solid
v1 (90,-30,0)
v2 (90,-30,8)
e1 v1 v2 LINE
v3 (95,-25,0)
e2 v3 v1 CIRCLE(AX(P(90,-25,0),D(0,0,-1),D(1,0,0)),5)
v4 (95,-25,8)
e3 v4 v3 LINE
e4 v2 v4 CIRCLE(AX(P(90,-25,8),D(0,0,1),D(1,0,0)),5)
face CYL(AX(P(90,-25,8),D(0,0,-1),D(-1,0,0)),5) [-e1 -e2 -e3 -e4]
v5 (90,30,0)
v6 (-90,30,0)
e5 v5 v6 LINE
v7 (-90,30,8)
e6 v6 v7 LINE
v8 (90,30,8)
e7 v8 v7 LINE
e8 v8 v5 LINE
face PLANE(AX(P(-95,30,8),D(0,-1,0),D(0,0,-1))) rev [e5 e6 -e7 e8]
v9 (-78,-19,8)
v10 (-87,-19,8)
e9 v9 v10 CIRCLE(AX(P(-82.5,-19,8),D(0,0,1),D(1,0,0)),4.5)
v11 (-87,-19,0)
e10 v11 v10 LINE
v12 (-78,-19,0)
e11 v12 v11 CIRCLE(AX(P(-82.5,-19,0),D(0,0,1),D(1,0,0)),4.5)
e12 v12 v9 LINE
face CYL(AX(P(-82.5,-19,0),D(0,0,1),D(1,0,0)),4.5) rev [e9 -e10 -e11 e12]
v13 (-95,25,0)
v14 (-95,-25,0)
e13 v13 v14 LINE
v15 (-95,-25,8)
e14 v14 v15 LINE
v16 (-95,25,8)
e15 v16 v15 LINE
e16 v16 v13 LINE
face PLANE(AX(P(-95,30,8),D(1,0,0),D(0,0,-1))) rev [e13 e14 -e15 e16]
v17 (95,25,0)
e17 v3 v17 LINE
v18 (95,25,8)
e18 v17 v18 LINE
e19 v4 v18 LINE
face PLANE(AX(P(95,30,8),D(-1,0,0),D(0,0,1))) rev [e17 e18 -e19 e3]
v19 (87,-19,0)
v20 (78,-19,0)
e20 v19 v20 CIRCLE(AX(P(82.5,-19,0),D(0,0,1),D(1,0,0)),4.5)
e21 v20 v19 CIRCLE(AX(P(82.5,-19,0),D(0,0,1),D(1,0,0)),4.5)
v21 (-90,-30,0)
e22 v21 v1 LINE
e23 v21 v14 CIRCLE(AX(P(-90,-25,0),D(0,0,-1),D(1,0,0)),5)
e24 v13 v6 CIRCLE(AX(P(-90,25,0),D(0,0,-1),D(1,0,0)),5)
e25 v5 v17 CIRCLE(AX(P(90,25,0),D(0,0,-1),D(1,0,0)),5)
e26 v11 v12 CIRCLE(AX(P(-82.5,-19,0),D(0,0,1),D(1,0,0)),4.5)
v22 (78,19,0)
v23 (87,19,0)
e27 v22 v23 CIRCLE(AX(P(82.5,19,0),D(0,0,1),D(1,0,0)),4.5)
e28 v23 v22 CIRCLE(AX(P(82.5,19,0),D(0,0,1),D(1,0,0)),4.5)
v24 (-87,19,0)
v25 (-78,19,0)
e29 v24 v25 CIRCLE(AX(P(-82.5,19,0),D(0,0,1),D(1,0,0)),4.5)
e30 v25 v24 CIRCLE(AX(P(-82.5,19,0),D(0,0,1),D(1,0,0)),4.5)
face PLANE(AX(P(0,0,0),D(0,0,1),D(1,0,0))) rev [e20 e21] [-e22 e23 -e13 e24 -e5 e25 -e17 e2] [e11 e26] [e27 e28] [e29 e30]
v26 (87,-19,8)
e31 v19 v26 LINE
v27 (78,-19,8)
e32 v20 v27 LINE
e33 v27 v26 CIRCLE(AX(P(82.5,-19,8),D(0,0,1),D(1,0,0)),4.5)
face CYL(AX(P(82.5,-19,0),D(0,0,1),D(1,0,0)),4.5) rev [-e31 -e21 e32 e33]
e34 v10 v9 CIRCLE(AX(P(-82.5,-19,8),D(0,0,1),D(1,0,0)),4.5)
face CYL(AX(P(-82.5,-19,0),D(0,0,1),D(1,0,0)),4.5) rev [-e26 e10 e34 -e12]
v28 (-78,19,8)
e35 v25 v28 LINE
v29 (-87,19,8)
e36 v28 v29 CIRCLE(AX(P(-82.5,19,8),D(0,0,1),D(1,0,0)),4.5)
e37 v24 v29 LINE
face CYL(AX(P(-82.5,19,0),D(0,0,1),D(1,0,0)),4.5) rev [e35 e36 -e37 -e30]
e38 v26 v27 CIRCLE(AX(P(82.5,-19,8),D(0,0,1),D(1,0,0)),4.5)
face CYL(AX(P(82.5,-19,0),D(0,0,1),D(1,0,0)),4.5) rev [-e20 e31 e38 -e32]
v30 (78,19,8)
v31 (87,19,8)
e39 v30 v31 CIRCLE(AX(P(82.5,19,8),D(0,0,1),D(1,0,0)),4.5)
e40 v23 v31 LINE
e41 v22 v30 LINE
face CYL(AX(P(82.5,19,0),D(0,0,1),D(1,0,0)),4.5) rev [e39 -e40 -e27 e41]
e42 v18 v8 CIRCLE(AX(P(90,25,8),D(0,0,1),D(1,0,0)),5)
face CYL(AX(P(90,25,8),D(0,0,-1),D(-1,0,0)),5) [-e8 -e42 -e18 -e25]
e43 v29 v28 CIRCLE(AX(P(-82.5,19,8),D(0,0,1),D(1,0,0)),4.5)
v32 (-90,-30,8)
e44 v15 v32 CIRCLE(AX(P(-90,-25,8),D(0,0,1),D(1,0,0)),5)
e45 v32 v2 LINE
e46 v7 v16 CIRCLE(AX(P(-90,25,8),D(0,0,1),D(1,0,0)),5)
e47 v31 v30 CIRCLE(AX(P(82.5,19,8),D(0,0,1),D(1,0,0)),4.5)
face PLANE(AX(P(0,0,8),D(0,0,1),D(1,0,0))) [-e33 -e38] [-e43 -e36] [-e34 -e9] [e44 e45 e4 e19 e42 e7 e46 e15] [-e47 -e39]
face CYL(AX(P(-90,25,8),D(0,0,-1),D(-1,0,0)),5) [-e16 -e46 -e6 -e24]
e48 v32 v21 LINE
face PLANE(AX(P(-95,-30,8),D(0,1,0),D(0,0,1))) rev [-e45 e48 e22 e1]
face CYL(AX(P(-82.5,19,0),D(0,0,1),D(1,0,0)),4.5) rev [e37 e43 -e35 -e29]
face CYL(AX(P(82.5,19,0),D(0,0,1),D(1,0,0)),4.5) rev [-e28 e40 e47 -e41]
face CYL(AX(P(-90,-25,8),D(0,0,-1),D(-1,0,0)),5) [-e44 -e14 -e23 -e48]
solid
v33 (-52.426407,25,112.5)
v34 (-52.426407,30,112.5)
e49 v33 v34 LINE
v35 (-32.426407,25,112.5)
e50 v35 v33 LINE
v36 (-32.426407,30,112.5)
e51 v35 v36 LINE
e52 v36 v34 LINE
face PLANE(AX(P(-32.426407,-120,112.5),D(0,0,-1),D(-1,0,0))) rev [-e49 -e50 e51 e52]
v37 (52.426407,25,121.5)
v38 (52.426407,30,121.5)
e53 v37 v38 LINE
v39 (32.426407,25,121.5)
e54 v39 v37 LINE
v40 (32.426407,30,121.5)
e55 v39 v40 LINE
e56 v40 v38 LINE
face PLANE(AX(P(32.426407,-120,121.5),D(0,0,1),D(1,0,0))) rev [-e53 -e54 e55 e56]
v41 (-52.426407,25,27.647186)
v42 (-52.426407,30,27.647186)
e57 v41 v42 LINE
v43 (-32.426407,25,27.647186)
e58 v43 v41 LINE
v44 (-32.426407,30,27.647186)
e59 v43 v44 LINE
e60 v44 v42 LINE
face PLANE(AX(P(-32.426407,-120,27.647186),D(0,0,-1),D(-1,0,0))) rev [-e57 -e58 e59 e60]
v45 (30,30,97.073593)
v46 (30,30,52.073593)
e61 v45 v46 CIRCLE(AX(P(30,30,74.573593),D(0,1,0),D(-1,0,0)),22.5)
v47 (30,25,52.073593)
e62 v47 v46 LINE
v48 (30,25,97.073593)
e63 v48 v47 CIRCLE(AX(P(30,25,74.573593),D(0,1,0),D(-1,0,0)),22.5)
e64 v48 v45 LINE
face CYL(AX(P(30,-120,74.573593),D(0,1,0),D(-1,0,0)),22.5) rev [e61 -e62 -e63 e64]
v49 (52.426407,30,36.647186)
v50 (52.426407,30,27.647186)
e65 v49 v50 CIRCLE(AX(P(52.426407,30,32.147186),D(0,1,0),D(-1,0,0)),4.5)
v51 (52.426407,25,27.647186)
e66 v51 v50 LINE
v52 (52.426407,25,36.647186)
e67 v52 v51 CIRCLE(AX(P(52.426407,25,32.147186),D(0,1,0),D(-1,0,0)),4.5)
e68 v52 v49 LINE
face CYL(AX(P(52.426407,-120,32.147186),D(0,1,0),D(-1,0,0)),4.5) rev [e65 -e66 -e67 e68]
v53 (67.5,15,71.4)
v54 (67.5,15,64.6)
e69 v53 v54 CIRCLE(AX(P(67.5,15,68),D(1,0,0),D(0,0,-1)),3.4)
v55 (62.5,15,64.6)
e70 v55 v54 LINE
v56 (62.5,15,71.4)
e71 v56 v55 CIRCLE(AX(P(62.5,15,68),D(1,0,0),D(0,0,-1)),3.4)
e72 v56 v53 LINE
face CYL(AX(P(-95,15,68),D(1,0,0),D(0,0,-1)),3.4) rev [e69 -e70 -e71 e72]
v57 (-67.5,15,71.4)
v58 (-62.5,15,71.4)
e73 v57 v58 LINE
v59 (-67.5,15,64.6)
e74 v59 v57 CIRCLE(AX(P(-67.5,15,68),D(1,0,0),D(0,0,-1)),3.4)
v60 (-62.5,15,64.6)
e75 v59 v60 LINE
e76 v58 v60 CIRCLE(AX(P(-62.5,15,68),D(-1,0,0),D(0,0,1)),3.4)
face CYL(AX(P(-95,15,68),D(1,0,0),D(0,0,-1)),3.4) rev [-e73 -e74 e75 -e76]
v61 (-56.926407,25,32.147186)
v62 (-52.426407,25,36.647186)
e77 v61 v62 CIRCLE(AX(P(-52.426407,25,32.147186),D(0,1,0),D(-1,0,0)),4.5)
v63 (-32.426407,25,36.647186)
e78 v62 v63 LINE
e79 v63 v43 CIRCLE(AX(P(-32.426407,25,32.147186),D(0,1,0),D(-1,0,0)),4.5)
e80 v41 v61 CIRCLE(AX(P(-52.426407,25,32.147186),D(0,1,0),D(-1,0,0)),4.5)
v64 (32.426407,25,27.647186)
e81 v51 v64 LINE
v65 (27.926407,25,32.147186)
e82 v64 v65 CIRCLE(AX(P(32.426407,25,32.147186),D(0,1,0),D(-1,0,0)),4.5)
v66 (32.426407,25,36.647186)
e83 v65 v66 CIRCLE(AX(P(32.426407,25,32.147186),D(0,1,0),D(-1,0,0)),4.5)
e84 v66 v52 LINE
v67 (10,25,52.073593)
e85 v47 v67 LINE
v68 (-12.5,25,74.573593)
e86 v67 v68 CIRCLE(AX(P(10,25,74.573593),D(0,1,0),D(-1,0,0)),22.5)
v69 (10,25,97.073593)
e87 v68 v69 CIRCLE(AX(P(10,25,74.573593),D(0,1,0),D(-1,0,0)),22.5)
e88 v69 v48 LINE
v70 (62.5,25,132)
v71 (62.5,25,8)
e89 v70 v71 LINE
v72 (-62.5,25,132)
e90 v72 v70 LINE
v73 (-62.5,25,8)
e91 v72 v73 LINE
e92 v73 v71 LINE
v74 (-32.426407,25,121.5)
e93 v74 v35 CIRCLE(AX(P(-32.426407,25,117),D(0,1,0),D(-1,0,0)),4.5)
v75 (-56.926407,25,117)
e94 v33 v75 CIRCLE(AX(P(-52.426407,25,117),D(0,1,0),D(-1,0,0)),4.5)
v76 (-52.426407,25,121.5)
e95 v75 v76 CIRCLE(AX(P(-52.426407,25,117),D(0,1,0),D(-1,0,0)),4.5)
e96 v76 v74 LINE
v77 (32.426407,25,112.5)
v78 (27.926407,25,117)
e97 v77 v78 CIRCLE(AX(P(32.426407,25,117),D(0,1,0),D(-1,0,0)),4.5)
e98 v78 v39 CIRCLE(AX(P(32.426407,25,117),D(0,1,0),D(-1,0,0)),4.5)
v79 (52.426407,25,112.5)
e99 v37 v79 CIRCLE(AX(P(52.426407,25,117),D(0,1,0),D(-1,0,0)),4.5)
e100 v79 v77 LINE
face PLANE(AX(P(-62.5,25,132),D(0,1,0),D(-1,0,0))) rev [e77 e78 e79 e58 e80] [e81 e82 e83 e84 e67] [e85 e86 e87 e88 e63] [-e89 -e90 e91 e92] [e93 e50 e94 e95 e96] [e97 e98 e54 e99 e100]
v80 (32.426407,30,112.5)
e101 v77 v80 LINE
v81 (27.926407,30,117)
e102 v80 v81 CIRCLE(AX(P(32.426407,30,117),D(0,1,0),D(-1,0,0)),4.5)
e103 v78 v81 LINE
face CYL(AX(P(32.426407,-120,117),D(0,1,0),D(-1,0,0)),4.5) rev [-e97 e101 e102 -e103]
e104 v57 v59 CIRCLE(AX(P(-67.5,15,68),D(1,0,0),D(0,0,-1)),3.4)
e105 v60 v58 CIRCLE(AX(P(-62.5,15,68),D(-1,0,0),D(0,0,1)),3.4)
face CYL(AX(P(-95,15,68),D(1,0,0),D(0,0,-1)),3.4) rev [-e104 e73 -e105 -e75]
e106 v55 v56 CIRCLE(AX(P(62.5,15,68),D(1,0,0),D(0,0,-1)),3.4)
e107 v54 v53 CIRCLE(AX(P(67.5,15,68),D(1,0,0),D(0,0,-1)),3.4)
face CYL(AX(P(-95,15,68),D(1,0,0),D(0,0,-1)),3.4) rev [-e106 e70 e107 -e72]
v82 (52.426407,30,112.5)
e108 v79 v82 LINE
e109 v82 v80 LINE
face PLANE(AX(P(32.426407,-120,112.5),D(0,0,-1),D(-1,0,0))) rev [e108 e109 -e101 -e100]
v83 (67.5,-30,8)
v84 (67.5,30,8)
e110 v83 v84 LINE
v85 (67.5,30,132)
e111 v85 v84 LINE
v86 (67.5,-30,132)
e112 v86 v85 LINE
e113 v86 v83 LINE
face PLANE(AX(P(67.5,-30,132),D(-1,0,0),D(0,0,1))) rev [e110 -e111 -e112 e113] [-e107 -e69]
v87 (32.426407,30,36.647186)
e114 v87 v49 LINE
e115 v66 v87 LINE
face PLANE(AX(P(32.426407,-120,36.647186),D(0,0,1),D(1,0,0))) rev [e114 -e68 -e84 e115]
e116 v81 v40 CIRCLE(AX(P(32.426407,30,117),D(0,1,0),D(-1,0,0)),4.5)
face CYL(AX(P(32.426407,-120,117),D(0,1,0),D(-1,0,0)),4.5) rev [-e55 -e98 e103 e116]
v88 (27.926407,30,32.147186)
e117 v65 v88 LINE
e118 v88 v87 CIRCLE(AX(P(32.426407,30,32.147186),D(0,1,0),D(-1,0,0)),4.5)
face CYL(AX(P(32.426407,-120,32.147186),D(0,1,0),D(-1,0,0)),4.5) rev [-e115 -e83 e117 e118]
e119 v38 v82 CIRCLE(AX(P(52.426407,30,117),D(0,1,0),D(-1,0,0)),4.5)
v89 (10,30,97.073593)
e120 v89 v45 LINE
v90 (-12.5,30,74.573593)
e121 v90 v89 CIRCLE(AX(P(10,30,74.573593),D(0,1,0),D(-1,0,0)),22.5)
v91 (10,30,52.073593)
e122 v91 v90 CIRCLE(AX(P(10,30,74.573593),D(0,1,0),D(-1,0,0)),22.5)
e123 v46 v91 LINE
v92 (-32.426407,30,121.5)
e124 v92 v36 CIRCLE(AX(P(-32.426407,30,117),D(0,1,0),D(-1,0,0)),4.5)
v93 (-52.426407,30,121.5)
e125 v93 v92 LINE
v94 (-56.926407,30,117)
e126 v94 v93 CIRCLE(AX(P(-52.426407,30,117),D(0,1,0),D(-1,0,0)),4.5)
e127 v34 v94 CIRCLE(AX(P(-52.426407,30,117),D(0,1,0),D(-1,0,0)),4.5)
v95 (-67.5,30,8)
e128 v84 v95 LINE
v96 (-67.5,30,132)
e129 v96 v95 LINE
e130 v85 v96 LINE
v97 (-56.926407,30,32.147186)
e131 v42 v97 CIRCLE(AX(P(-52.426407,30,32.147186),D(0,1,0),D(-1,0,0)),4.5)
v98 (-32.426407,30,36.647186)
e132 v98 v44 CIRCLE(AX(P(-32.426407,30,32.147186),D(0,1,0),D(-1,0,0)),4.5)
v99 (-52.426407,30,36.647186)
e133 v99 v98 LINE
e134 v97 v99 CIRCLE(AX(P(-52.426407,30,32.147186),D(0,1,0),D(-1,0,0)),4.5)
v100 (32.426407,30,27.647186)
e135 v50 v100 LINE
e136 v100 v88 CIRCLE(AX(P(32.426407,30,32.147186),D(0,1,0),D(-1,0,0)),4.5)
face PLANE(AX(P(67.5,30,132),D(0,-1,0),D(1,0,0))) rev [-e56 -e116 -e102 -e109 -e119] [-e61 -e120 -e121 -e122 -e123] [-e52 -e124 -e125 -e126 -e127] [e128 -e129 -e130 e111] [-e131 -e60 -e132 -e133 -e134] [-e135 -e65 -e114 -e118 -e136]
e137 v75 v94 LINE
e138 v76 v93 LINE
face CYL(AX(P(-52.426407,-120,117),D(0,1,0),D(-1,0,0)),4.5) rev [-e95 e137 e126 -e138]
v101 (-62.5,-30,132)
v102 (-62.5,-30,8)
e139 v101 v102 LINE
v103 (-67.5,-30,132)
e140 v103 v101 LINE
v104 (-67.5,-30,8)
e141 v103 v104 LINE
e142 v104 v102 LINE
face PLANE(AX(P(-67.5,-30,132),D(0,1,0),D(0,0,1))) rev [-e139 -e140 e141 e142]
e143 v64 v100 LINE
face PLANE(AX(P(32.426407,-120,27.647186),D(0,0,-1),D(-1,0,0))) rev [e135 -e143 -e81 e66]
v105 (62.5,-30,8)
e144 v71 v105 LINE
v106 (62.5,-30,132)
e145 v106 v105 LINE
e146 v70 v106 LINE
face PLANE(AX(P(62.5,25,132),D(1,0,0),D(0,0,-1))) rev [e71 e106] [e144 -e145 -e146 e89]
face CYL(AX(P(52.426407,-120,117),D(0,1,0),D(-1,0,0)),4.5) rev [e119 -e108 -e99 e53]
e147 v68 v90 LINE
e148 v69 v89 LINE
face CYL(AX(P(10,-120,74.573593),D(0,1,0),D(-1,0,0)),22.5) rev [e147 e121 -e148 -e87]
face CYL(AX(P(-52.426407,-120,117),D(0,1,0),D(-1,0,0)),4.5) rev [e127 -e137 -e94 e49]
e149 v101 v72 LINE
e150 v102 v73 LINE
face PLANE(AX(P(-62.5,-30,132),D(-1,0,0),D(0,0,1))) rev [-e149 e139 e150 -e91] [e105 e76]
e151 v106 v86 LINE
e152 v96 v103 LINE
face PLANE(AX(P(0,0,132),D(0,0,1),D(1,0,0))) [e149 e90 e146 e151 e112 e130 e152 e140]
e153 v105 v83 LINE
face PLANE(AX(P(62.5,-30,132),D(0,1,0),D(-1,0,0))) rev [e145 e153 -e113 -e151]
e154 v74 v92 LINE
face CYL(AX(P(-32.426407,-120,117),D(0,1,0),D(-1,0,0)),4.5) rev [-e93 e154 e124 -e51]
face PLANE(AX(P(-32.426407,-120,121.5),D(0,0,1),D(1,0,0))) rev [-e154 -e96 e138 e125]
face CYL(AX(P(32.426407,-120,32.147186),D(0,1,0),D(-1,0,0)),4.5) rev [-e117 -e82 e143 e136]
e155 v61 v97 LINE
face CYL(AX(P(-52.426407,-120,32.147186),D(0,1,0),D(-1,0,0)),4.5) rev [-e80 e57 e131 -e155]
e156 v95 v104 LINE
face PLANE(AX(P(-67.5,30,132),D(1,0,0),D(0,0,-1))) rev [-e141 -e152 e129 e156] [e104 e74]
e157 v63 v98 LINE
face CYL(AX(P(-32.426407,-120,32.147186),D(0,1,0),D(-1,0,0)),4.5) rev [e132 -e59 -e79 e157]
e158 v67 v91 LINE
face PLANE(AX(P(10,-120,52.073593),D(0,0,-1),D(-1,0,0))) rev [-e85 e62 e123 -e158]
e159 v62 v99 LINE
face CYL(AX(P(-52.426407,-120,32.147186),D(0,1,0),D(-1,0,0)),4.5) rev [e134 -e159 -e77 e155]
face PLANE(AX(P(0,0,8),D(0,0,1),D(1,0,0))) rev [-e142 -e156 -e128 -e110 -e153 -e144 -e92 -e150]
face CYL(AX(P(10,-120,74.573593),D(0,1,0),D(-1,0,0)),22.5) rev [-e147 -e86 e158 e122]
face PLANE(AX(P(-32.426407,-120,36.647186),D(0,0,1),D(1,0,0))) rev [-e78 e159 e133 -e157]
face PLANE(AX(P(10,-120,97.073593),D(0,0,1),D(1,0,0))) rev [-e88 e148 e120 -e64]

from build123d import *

# Parameters (mm, degrees)
SKETCH_1_W          = 190
SKETCH_1_H          = 60
EXTRUDE_1_DEPTH     = 8
SKETCH_2_R          = 4.5
CUT_EXTRUDE_1_DEPTH = 8
EXTRUDE_2_DEPTH     = 124
CUT_EXTRUDE_2_DEPTH = 150
FILLET_1_R          = 5
SKETCH_5_R          = 3.4
CUT_EXTRUDE_3_DEPTH = 212.495271815


with BuildPart() as part:
    # 草图1 → 凸台-拉伸1 (new body)
    with BuildSketch(Plane.XY):
        Rectangle(SKETCH_1_W, SKETCH_1_H)
    extrude(amount=EXTRUDE_1_DEPTH)

    # 草图2 → 切除-拉伸1 (cut)
    with BuildSketch(Plane.XY.offset(8)):
        with Locations((-82.5, 19)):
            Circle(SKETCH_2_R)
        with Locations((82.5, 19)):
            Circle(SKETCH_2_R)
        with Locations((82.5, -19)):
            Circle(SKETCH_2_R)
        with Locations((-82.5, -19)):
            Circle(SKETCH_2_R)
    extrude(amount=-CUT_EXTRUDE_1_DEPTH, mode=Mode.SUBTRACT)

    # 圆角1
    fillet_1_edges = [part.edges().sort_by_distance(p)[0] for p in [
        (95, -30, 4),
        (-95, -30, 4),
        (-95, 30, 4),
        (95, 30, 4),
    ]]
    fillet(fillet_1_edges, radius=FILLET_1_R)


with BuildPart() as body_2:
    # 草图3 → 凸台-拉伸2 (new body)
    with BuildSketch(Plane.XY.offset(8)):
        Polygon((-67.5, 30), (-67.5, -30), (-62.5, -30), (-62.5, 25), (62.5, 25), (62.5, -30), (67.5, -30), (67.5, 30), align=None)
    extrude(amount=EXTRUDE_2_DEPTH)

    # 草图4 → 切除-拉伸2 (cut)
    with BuildSketch(Plane(origin=(0, 30, 0), x_dir=(1, 0, 0), z_dir=(0, 1, 0))):
        with BuildLine():
            Line((-32.426406871, -112.5), (-52.426406871, -112.5))
            ThreePointArc((-52.426406871, -112.5), (-56.926406871, -117), (-52.426406871, -121.5))
            Line((-52.426406871, -121.5), (-32.426406871, -121.5))
            ThreePointArc((-32.426406871, -121.5), (-27.926406871, -117), (-32.426406871, -112.5))
        make_face()
        with BuildLine():
            Line((-32.426406871, -36.647186258), (-52.426406871, -36.647186258))
            ThreePointArc((-52.426406871, -36.647186258), (-56.926406871, -32.147186258), (-52.426406871, -27.647186258))
            Line((-52.426406871, -27.647186258), (-32.426406871, -27.647186258))
            ThreePointArc((-32.426406871, -27.647186258), (-27.926406871, -32.147186258), (-32.426406871, -36.647186258))
        make_face()
        with BuildLine():
            Line((32.426406871, -27.647186258), (52.426406871, -27.647186258))
            ThreePointArc((52.426406871, -27.647186258), (56.926406871, -32.147186258), (52.426406871, -36.647186258))
            Line((52.426406871, -36.647186258), (32.426406871, -36.647186258))
            ThreePointArc((32.426406871, -36.647186258), (27.926406871, -32.147186258), (32.426406871, -27.647186258))
        make_face()
        with BuildLine():
            Line((32.426406871, -112.5), (52.426406871, -112.5))
            ThreePointArc((52.426406871, -112.5), (56.926406871, -117), (52.426406871, -121.5))
            Line((52.426406871, -121.5), (32.426406871, -121.5))
            ThreePointArc((32.426406871, -121.5), (27.926406871, -117), (32.426406871, -112.5))
        make_face()
        with BuildLine():
            Line((10, -52.073593129), (30, -52.073593129))
            ThreePointArc((30, -52.073593129), (52.5, -74.573593129), (30, -97.073593129))
            Line((30, -97.073593129), (10, -97.073593129))
            ThreePointArc((10, -97.073593129), (-12.5, -74.573593129), (10, -52.073593129))
        make_face()
    extrude(amount=-CUT_EXTRUDE_2_DEPTH, mode=Mode.SUBTRACT)

    # 草图5 → 切除-拉伸3 (cut, through all)
    with BuildSketch(Plane(origin=(67.5, 0, 0), x_dir=(0, 0, -1), z_dir=(1, 0, 0))):
        with Locations((-68, 15)):
            Circle(SKETCH_5_R)
    extrude(amount=-CUT_EXTRUDE_3_DEPTH, mode=Mode.SUBTRACT)


solid = Compound([part.part, body_2.part])
